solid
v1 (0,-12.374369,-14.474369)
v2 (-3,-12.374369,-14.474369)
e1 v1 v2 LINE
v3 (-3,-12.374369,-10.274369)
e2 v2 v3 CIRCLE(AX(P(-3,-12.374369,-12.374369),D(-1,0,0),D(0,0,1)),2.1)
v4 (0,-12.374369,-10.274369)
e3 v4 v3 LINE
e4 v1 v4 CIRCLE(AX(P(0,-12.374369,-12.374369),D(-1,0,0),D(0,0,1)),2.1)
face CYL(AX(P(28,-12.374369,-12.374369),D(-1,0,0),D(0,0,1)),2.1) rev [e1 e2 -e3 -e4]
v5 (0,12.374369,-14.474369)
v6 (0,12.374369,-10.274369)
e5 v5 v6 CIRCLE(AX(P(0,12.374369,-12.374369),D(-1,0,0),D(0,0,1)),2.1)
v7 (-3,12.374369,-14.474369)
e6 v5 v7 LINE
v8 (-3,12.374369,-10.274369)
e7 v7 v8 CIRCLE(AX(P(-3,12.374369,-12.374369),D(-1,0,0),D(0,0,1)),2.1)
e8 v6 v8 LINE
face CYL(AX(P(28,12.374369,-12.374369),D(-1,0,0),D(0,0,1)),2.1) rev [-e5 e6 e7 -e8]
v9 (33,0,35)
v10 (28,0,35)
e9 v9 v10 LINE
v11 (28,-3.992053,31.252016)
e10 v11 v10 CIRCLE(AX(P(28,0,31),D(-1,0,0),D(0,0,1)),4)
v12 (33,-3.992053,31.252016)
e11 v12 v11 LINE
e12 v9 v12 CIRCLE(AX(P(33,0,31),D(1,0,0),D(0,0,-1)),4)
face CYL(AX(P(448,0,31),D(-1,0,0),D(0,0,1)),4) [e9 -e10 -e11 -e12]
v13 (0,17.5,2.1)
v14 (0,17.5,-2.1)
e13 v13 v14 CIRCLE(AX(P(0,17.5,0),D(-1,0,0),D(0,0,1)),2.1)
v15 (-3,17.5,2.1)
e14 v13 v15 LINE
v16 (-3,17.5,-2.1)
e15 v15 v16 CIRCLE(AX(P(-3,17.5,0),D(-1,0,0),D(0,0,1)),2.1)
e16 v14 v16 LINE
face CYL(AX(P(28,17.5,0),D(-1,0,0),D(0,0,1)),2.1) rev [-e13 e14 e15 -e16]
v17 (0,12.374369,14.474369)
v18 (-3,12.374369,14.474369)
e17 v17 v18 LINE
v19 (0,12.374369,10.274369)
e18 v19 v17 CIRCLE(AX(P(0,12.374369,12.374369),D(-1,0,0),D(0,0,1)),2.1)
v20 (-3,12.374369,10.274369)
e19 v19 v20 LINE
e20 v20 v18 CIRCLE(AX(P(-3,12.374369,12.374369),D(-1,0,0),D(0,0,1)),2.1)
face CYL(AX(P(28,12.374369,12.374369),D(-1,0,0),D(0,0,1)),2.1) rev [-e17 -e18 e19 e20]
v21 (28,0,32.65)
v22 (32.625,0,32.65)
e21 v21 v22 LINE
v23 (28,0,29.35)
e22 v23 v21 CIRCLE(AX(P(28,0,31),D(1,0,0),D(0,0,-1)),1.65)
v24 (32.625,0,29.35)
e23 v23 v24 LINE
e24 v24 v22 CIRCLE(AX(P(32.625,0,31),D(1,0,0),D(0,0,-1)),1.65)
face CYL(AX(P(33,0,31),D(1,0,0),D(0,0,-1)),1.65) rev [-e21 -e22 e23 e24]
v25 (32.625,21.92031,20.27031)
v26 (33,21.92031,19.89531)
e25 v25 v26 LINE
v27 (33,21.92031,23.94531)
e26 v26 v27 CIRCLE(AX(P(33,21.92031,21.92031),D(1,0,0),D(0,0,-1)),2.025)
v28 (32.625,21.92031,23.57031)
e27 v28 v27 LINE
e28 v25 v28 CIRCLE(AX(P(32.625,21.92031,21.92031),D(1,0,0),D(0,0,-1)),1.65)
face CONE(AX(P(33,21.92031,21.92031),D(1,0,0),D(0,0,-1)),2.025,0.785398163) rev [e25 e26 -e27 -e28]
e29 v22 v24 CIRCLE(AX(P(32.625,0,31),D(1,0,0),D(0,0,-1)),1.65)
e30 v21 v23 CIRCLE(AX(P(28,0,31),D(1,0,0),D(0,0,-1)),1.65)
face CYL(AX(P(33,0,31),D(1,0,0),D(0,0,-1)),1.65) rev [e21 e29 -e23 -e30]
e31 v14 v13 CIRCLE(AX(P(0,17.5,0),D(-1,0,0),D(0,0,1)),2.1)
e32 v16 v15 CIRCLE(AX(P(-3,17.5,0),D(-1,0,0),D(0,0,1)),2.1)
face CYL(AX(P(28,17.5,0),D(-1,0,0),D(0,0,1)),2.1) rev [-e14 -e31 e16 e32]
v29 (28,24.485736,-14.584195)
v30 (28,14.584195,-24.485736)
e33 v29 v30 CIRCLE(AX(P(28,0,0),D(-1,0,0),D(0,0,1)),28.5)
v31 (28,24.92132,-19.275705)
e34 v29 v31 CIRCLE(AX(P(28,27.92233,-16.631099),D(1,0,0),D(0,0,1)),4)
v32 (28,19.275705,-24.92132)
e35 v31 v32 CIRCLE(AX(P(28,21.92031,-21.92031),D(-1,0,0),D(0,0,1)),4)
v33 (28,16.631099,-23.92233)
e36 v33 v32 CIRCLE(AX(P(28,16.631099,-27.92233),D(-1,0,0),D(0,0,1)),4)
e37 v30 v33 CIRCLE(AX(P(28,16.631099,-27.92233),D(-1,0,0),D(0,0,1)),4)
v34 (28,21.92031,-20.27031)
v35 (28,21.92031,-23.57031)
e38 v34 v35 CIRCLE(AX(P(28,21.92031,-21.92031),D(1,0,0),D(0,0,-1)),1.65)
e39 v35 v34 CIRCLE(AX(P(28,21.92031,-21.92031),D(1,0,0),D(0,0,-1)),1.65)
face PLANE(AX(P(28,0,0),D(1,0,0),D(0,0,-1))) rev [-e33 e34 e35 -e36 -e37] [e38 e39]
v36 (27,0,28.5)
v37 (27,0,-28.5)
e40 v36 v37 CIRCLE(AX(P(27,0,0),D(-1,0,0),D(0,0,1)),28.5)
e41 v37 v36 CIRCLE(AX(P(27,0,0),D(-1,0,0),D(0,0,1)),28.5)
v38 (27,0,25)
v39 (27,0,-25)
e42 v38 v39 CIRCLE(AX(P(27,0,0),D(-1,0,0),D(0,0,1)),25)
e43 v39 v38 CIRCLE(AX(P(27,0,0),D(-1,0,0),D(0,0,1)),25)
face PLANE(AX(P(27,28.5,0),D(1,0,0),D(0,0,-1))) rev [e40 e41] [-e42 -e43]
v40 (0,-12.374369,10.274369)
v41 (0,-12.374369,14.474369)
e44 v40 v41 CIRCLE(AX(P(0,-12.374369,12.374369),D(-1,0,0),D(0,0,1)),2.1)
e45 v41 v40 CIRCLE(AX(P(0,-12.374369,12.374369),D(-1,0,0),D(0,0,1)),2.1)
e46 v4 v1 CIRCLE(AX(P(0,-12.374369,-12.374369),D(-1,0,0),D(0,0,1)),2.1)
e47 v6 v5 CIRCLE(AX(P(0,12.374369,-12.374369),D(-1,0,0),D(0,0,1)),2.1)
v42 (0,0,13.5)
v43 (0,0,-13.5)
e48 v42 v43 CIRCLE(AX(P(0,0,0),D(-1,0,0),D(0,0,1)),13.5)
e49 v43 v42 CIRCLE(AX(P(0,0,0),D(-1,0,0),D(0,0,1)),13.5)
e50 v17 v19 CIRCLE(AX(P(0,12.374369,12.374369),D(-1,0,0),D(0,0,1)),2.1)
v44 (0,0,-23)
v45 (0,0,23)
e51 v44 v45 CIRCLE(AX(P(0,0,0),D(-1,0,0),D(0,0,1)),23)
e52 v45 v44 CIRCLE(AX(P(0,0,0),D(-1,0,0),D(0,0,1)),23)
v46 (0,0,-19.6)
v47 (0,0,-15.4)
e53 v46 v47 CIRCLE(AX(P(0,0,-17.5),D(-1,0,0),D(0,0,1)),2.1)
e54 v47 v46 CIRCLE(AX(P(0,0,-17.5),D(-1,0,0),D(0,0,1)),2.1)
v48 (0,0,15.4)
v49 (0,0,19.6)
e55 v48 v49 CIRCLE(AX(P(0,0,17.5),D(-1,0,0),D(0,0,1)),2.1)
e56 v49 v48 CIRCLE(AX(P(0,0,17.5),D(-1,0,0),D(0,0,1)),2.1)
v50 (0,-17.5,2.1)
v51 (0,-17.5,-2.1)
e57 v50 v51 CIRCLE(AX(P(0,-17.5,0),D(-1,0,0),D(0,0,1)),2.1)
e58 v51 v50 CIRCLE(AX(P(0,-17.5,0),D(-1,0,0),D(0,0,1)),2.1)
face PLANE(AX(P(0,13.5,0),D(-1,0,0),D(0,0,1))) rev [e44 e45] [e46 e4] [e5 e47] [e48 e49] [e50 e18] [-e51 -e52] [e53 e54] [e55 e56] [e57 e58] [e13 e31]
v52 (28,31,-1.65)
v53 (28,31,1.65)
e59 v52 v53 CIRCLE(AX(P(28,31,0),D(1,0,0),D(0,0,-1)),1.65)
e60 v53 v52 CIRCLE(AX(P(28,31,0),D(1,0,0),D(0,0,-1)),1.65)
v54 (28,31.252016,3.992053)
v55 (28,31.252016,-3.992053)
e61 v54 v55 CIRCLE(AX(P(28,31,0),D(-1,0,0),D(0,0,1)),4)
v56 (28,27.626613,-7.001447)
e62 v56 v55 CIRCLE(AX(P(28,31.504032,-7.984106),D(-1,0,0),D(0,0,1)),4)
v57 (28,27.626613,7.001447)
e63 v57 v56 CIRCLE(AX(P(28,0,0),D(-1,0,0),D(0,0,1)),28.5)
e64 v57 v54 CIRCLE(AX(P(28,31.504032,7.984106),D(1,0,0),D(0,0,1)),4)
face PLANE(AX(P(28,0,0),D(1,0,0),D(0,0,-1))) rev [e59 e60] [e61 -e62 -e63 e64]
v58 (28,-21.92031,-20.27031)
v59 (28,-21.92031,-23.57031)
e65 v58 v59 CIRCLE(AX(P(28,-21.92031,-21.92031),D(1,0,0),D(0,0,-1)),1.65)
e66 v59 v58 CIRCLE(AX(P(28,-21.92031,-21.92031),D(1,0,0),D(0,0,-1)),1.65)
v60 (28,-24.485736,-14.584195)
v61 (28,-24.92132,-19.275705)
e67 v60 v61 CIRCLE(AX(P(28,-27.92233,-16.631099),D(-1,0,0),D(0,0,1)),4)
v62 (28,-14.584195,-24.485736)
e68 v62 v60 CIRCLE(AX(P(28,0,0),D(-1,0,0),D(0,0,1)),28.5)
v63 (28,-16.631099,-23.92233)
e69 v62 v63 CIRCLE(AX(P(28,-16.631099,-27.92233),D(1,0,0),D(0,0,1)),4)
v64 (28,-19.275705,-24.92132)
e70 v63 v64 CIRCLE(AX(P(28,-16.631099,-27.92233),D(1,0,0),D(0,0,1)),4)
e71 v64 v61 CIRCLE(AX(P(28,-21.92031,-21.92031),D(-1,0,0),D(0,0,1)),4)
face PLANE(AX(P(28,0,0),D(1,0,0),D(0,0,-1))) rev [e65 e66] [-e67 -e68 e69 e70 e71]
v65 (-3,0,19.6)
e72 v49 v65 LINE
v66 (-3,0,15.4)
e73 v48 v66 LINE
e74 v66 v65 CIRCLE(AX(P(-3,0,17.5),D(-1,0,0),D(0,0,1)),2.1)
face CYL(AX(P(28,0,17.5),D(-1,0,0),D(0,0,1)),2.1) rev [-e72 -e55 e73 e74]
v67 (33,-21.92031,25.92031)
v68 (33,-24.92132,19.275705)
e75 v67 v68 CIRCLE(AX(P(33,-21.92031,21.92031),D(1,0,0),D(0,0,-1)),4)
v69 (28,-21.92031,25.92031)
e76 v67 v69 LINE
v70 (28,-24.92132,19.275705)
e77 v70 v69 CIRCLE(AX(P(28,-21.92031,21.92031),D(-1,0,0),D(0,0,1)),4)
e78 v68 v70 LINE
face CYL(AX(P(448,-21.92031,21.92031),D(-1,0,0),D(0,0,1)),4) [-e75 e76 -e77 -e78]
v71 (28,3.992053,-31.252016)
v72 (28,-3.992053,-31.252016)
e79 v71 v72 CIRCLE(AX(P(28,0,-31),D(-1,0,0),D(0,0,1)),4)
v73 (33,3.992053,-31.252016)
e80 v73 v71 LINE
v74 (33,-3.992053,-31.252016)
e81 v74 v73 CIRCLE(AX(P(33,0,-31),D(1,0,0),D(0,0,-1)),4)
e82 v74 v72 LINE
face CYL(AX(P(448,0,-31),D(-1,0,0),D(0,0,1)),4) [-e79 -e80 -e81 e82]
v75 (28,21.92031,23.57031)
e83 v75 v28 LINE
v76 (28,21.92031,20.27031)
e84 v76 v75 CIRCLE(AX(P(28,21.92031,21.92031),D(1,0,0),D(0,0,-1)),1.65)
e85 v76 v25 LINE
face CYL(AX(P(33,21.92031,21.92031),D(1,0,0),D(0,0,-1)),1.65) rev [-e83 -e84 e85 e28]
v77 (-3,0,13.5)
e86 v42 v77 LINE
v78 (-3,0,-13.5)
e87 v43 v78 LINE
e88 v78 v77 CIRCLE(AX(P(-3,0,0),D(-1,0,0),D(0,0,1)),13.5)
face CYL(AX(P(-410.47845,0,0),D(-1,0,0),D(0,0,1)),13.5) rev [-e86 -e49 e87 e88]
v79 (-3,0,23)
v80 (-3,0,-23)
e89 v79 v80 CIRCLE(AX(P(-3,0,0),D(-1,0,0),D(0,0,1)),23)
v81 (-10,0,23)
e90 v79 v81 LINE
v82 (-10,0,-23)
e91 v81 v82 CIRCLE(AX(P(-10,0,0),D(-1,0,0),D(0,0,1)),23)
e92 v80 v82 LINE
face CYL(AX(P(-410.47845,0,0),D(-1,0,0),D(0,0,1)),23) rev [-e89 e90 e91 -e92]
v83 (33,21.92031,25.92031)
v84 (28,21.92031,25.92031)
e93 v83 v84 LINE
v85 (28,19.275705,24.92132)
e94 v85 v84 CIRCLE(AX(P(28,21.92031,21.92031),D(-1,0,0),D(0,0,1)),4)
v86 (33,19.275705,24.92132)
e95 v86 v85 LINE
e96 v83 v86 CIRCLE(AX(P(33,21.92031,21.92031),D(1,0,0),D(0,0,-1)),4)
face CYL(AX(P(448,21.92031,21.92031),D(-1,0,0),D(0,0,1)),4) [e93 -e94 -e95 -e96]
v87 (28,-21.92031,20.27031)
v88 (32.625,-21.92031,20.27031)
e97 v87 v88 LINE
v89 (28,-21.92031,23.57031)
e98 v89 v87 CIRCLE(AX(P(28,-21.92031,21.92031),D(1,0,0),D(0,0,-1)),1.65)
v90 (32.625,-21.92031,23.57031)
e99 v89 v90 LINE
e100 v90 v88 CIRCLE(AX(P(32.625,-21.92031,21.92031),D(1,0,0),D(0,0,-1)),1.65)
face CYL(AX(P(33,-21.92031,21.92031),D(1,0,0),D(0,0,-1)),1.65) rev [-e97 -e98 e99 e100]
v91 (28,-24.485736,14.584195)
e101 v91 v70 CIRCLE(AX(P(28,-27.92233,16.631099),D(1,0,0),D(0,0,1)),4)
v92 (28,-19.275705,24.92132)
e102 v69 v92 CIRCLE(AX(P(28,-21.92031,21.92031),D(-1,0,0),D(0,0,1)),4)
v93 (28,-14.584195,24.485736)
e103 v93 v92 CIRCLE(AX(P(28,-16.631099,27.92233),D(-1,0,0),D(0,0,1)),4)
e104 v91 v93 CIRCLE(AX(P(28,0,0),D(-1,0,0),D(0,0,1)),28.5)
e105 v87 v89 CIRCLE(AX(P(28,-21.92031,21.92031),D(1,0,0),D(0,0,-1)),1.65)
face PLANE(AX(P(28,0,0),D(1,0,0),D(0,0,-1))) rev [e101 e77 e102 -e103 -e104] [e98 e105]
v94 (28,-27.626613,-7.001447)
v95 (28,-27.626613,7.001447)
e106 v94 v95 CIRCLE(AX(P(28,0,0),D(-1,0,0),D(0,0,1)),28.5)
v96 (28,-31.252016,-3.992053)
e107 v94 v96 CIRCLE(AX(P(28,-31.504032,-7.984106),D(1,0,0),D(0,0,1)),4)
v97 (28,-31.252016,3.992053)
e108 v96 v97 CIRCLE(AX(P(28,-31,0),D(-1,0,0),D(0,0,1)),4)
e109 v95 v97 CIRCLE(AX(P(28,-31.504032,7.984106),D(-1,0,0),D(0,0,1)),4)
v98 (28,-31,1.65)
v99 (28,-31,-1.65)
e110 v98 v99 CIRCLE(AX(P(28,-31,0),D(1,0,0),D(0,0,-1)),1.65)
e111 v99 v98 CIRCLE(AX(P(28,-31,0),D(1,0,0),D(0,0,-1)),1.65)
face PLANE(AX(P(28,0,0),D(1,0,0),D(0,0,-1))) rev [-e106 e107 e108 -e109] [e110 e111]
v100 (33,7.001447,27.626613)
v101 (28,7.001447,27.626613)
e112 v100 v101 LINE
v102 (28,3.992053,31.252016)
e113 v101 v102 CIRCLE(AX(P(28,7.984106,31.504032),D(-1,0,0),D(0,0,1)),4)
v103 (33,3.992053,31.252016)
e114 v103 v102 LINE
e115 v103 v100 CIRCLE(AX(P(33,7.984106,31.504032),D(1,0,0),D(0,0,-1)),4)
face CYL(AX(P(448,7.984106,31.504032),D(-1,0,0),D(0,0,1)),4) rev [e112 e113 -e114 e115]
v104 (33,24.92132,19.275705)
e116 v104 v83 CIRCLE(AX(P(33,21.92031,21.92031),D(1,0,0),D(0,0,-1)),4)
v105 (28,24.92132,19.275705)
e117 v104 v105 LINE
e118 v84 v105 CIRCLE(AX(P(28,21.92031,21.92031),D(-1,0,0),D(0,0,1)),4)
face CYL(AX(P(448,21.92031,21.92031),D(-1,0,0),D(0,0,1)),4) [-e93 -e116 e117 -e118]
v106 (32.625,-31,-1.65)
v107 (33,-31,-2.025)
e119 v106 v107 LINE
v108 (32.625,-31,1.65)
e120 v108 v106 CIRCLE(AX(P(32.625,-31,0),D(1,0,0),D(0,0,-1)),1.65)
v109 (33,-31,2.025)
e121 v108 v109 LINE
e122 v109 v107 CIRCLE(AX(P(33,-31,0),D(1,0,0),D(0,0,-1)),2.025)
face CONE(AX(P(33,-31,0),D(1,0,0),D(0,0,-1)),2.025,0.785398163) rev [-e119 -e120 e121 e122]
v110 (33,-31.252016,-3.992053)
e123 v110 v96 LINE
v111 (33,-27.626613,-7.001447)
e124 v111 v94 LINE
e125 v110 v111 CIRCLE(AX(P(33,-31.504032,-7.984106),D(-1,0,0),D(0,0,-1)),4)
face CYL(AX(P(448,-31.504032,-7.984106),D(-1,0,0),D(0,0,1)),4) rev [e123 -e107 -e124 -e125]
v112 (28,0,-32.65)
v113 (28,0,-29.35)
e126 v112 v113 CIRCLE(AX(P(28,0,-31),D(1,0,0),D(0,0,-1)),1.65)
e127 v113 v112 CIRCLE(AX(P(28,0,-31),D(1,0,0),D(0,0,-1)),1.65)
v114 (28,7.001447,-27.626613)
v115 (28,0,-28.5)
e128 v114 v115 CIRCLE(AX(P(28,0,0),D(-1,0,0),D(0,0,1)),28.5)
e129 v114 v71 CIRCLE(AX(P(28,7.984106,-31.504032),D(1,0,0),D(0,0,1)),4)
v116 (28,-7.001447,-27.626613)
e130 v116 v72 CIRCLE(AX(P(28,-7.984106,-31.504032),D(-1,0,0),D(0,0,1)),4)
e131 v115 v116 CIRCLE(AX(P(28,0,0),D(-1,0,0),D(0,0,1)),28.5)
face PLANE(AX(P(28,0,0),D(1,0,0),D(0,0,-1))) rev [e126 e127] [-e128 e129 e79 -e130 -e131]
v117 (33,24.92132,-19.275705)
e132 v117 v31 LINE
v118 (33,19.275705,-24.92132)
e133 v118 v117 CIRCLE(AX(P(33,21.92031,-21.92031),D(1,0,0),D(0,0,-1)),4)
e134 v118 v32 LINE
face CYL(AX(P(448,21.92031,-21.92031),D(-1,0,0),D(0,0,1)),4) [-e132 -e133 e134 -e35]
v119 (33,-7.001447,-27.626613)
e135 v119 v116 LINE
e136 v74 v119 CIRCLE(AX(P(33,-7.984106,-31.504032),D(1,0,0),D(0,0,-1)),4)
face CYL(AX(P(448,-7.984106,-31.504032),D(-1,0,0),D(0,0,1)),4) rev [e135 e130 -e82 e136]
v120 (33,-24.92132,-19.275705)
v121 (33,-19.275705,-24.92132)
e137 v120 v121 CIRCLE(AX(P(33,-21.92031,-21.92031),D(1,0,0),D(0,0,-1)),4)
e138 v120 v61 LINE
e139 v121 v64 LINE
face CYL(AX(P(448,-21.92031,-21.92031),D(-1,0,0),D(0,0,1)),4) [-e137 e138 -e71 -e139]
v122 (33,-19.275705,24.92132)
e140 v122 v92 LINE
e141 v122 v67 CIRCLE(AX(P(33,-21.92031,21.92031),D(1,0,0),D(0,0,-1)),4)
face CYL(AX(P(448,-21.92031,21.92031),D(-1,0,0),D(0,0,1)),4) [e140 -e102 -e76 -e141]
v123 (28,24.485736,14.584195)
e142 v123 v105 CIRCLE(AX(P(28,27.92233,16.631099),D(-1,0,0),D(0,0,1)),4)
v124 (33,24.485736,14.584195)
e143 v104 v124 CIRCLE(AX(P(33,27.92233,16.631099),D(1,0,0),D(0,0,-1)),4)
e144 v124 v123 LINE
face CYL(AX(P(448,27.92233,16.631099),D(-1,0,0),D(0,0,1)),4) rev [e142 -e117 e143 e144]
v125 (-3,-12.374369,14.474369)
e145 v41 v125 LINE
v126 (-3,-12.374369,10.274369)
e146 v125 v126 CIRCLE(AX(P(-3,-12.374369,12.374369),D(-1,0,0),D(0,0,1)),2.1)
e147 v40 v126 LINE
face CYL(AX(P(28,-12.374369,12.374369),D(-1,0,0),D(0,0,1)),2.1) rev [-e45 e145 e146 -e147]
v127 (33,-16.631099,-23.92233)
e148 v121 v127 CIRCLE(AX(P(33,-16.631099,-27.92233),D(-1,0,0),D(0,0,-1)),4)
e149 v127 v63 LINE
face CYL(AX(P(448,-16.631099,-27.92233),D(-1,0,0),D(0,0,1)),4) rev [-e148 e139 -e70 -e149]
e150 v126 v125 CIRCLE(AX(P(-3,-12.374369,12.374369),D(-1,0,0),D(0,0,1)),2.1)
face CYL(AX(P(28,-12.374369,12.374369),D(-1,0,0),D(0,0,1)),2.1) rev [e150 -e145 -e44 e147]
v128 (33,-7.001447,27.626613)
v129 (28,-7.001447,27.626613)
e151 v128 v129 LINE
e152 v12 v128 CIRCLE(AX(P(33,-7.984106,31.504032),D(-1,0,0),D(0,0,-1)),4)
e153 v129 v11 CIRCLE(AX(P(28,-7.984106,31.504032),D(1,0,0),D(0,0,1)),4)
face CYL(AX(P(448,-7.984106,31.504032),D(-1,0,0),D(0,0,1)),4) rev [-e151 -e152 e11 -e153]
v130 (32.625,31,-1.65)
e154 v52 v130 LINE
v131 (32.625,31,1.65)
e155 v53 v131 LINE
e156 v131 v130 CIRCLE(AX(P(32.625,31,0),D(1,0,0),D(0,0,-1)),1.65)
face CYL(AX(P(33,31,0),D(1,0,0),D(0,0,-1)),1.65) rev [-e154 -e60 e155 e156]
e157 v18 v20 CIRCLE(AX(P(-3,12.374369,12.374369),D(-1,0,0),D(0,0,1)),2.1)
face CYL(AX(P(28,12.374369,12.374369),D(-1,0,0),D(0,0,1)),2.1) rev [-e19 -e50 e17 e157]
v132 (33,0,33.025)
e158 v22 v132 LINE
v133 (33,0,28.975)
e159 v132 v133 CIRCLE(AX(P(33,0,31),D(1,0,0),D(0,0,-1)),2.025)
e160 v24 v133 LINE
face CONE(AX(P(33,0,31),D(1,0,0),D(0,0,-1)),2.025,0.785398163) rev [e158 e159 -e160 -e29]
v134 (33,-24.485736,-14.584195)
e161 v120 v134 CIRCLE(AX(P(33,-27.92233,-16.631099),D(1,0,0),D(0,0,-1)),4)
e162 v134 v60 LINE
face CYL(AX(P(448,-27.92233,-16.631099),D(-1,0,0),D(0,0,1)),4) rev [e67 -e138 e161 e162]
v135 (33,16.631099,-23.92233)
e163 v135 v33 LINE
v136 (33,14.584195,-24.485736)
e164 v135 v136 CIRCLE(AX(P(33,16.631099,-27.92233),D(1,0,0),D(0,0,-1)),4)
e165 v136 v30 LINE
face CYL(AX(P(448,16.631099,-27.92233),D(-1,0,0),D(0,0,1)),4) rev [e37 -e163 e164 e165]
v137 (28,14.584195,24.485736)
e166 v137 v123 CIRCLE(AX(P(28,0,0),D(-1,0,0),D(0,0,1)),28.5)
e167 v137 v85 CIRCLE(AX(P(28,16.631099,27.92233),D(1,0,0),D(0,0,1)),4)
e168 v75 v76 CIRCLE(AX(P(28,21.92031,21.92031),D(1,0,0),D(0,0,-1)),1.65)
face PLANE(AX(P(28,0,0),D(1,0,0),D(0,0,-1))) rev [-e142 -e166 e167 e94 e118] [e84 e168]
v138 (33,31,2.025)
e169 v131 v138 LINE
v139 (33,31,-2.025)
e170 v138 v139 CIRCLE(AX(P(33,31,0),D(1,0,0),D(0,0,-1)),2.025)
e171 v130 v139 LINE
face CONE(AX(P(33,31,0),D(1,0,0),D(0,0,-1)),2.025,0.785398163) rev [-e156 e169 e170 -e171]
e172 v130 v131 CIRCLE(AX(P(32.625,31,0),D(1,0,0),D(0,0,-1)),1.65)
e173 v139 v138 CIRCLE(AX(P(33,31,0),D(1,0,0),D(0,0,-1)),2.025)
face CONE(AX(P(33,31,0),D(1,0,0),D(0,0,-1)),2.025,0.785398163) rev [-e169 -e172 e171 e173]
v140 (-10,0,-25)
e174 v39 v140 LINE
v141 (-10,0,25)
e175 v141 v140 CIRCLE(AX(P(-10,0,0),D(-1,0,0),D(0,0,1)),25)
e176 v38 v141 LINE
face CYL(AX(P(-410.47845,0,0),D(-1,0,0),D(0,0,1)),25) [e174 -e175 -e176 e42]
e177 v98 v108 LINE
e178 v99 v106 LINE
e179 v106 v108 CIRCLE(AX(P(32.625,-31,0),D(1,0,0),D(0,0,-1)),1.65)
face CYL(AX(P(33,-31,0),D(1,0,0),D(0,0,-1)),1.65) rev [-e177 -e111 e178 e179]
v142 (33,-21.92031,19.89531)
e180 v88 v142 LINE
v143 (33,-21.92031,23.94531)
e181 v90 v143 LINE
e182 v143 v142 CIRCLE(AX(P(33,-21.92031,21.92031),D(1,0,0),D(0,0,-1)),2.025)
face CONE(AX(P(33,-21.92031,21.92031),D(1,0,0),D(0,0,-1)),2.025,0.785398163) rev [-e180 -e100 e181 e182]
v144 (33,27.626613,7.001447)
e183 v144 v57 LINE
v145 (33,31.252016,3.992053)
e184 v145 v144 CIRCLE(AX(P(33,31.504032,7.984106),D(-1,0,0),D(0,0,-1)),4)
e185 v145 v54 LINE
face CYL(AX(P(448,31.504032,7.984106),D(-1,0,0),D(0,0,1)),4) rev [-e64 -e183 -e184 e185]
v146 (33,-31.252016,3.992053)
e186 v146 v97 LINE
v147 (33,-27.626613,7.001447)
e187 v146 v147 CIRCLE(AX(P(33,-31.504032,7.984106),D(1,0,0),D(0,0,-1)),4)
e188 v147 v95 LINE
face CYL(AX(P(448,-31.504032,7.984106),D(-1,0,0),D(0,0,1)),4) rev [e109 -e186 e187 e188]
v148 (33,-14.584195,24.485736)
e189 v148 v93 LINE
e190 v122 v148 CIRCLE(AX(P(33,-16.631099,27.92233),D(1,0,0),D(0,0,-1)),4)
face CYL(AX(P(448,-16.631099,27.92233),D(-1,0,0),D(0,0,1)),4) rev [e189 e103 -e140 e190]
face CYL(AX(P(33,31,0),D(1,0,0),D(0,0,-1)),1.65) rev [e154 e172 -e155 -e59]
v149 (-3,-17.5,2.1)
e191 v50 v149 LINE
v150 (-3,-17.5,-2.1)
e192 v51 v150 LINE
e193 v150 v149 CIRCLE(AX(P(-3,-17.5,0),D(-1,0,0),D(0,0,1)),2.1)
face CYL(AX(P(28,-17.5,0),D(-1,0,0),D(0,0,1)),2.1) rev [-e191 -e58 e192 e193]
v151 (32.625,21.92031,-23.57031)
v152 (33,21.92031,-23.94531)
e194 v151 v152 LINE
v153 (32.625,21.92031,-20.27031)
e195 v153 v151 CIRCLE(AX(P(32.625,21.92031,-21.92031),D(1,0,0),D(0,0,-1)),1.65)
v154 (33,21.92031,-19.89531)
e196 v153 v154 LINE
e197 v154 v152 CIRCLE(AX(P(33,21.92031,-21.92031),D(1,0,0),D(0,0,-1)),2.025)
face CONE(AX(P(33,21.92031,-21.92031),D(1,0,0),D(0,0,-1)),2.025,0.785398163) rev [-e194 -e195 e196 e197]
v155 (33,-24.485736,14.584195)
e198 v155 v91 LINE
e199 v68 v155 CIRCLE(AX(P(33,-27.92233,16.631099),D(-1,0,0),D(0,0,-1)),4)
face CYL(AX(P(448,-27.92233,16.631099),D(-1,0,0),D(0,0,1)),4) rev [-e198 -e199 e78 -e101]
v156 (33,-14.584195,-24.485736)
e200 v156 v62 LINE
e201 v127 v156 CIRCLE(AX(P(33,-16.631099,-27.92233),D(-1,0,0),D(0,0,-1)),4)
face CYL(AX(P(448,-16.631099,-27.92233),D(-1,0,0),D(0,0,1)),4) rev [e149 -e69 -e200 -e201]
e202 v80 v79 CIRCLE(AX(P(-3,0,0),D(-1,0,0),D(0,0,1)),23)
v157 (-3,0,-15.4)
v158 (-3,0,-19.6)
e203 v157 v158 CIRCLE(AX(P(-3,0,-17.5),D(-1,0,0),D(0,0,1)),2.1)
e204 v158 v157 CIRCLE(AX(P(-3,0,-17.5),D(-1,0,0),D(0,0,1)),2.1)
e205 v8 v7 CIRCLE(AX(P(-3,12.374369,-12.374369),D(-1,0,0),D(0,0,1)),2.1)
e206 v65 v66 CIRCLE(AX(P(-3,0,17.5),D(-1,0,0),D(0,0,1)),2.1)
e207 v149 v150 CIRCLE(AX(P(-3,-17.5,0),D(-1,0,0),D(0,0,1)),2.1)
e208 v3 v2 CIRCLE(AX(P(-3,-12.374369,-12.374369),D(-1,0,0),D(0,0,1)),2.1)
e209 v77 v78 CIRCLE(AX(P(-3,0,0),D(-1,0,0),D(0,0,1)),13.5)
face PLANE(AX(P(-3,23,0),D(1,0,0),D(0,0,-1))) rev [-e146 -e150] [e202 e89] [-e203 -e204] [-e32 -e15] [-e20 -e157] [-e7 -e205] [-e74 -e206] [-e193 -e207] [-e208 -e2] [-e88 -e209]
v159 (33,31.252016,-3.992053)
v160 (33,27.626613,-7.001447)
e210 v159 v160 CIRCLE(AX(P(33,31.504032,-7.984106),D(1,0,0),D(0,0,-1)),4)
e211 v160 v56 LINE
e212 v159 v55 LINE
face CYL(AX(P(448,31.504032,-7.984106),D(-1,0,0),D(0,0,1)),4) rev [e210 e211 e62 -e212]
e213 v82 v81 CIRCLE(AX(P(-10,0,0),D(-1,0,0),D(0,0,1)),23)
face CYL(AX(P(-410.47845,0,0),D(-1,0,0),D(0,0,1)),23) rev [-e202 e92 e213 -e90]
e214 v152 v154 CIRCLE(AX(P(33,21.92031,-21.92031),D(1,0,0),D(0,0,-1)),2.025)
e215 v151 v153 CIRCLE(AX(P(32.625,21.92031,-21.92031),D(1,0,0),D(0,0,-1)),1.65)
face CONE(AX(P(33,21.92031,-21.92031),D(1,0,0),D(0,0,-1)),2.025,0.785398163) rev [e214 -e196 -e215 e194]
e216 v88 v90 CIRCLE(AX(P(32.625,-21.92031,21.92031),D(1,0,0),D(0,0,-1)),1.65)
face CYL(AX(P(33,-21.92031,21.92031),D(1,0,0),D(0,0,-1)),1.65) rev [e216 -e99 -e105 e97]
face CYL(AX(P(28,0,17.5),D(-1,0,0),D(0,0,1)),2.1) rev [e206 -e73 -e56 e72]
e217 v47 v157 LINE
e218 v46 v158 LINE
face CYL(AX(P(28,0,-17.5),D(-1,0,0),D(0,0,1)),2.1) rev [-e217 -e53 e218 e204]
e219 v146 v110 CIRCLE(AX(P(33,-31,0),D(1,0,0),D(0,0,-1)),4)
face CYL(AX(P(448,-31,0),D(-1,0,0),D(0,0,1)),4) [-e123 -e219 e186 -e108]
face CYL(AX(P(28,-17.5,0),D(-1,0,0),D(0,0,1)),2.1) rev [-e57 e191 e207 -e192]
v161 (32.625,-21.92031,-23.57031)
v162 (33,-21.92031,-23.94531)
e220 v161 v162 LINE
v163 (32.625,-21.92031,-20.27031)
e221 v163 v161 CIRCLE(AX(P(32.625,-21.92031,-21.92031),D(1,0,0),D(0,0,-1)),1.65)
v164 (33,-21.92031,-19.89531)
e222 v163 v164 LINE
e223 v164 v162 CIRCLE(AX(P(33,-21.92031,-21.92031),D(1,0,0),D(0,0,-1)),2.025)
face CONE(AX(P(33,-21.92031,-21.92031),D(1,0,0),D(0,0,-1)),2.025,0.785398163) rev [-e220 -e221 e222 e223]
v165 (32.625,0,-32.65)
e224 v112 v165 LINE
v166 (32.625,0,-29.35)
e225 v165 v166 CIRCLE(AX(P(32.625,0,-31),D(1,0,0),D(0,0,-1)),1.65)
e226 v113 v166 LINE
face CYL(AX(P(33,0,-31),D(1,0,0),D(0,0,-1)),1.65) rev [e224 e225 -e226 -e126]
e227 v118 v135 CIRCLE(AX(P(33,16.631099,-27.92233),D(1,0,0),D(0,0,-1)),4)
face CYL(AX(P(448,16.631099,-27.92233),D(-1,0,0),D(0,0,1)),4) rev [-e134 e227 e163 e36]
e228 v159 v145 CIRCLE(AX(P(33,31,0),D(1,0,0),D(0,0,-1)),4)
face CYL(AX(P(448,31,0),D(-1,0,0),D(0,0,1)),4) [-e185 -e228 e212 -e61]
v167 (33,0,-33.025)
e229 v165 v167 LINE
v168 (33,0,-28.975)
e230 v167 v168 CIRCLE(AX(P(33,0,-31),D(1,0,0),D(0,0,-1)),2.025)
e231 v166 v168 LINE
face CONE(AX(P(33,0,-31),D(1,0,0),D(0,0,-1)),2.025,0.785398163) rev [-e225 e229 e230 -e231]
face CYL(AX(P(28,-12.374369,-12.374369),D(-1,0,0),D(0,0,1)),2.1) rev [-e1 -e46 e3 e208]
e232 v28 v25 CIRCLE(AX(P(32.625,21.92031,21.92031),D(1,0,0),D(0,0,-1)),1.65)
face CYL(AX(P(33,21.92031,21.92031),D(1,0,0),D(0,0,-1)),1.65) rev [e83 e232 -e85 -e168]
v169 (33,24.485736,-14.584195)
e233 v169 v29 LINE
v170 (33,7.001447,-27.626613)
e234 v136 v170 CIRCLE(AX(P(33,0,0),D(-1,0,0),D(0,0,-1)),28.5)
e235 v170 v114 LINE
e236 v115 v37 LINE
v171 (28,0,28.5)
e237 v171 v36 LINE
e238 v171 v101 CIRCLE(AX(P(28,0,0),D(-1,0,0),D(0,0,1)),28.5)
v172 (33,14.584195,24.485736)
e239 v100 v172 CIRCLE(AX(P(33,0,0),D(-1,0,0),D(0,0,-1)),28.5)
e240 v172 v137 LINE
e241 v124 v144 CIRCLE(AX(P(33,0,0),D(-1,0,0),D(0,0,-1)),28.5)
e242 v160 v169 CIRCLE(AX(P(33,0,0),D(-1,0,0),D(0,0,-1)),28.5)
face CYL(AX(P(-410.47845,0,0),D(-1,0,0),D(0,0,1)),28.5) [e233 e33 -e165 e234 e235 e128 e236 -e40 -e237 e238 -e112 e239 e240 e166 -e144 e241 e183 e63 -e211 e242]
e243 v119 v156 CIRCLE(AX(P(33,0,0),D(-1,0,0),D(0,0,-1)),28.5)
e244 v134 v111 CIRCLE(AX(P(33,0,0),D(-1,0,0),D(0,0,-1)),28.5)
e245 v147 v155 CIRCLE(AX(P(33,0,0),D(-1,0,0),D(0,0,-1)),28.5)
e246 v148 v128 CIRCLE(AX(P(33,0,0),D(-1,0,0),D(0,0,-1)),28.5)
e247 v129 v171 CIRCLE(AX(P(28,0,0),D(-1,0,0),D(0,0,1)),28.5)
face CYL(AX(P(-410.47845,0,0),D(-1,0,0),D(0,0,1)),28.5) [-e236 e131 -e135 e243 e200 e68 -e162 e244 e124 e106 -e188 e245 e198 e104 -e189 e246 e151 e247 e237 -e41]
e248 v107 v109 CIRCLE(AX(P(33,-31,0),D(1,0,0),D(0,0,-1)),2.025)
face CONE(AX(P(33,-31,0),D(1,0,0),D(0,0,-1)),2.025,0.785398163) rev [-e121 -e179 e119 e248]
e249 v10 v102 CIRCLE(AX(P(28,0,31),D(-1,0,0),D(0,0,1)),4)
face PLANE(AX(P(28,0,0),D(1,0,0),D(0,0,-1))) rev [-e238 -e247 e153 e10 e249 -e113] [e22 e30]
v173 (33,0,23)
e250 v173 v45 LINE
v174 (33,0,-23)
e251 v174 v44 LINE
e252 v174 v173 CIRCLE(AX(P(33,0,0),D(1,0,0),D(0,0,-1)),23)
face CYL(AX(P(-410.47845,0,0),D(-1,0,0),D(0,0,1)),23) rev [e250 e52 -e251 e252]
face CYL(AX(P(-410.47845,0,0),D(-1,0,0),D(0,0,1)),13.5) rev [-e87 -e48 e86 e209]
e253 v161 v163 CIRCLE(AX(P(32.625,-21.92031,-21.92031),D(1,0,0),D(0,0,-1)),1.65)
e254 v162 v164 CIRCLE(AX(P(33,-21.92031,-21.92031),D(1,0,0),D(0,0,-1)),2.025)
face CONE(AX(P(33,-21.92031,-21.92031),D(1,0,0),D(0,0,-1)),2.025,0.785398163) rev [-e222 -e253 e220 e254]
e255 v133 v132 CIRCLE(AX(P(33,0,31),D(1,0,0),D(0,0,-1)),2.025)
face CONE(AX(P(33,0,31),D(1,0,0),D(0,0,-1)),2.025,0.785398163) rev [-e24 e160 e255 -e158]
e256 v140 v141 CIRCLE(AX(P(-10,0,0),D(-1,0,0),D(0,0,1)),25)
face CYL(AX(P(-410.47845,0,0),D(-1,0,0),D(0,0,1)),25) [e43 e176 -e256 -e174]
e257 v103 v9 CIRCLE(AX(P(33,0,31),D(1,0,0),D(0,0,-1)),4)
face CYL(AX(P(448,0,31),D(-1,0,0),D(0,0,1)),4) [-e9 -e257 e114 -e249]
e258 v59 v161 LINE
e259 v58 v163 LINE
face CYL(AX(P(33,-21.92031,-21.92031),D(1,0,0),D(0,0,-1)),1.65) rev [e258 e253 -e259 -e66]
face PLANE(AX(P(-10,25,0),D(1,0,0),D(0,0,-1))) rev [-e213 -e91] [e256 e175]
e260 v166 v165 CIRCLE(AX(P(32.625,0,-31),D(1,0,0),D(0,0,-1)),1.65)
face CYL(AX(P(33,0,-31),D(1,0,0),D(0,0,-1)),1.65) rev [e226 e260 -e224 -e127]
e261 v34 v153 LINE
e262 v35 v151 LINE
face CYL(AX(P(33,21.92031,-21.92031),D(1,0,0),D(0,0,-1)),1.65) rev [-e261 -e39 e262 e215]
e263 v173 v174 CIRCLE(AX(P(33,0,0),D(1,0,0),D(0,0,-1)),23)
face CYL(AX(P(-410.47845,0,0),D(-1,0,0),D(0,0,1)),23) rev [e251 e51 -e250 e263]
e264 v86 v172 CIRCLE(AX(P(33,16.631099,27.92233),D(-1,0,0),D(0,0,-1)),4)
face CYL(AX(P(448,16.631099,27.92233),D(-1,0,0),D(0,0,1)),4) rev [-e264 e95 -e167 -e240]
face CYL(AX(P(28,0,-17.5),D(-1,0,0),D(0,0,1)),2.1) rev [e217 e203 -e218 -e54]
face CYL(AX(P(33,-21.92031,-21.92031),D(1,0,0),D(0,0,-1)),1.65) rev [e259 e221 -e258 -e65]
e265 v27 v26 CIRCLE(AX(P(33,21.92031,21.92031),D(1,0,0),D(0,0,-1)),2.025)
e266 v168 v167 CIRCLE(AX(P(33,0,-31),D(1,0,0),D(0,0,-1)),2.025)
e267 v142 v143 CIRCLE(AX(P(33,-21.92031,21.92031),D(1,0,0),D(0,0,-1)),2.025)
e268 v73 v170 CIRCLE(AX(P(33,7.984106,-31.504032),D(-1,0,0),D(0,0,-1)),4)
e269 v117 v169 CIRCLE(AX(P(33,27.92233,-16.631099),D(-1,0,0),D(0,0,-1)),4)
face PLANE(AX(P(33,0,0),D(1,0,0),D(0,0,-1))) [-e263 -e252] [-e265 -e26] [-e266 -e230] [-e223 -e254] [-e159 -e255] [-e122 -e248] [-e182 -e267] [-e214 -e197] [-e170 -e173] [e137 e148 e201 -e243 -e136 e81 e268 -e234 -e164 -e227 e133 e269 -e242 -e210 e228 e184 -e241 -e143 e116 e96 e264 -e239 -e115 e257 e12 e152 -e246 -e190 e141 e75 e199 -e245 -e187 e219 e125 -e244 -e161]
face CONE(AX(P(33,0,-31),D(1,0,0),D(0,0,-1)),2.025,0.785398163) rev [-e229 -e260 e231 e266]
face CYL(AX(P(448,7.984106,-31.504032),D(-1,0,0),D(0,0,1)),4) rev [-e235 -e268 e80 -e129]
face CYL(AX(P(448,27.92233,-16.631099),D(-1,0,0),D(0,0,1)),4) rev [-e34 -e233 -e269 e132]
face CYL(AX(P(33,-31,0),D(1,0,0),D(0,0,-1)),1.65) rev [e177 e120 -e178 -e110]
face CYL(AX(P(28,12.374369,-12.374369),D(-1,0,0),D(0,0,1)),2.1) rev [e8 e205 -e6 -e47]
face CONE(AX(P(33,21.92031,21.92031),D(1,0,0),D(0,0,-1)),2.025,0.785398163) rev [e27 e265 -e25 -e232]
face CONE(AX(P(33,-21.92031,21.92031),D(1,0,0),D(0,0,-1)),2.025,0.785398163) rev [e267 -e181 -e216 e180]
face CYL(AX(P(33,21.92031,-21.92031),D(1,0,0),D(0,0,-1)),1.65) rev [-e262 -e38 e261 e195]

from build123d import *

# Parameters (mm, degrees)
SKETCH_2_R                   = 2.1
CUT_EXTRUDE_1_DEPTH          = 51.847812146
EXTRUDE_START                = 5
SKETCH_3_R                   = 35
SKETCH_3_R_2                 = 23
EXTRUDE_1_DEPTH              = 5
HOLE_WIZARD_M4_1_D           = 3.3
HOLE_WIZARD_M4_1_CSINK_D     = 4.05
HOLE_WIZARD_M4_1_CSINK_ANGLE = 90
CUT_EXTRUDE_3_DEPTH          = 420


with BuildPart() as part:
    # 草图1 → 旋转1 (revolve)
    with BuildSketch(Plane.XY, mode=Mode.PRIVATE) as revolve_1_sk:
        Polygon((0, 13.5), (0, 23), (28, 23), (28, 28.5), (27, 28.5), (27, 25), (-10, 25), (-10, 23), (-3, 23), (-3, 13.5), align=None)
    revolve(revolve_1_sk.sketch.rotate(Axis((-410.478449984, 0, 0), (1, 0, 0)), 90), axis=Axis((-410.478449984, 0, 0), (1, 0, 0)))

    # 草图2 → 切除-拉伸1 (cut, through all)
    with BuildSketch(Plane.ZY.offset(3)):
        with Locations((0, 17.5)):
            Circle(SKETCH_2_R)
        with Locations((12.374368671, 12.374368671)):
            Circle(SKETCH_2_R)
        with Locations((17.5, 0)):
            Circle(SKETCH_2_R)
        with Locations((12.374368671, -12.374368671)):
            Circle(SKETCH_2_R)
        with Locations((0, -17.5)):
            Circle(SKETCH_2_R)
        with Locations((-12.374368671, -12.374368671)):
            Circle(SKETCH_2_R)
        with Locations((-17.5, 0)):
            Circle(SKETCH_2_R)
        with Locations((-12.374368671, 12.374368671)):
            Circle(SKETCH_2_R)
    extrude(amount=-CUT_EXTRUDE_1_DEPTH, mode=Mode.SUBTRACT)

    # 草图3 → 凸台-拉伸1 (add)
    with BuildSketch(Plane(origin=(28, 0, 0), x_dir=(0, 0, -1), z_dir=(1, 0, 0)).offset(EXTRUDE_START)):
        Circle(SKETCH_3_R)
        with Locations(Location((0, 0, 0), (0, 0, 180))):
            Circle(SKETCH_3_R_2, mode=Mode.SUBTRACT)
    extrude(amount=-EXTRUDE_1_DEPTH)

    # M4 螺纹孔1 (through all)
    with Locations(Plane(origin=(33, 0, 0), x_dir=(0, 0, -1), z_dir=(1, 0, 0))):
        with Locations((-21.920310217, 21.920310217), (0, 31), (21.920310217, 21.920310217), (31, 0), (21.920310217, -21.920310217), (0, -31), (-21.920310217, -21.920310217), (-31, 0)):
            CounterSinkHole(HOLE_WIZARD_M4_1_D / 2, HOLE_WIZARD_M4_1_CSINK_D / 2, counter_sink_angle=HOLE_WIZARD_M4_1_CSINK_ANGLE)

    # 草图9 → 切除-拉伸3 (cut)
    with BuildSketch(Plane.ZY.offset(-28)):
        with BuildLine():
            ThreePointArc((0, 35), (2.737876502, 33.916167392), (3.99205309, 31.252016129))
            ThreePointArc((3.99205309, 31.252016129), (4.90631025, 28.949199149), (7.001446957, 27.626612903))
            ThreePointArc((7.001446957, 27.626612903), (10.906477822, 26.330566677), (14.584194703, 24.485735947))
            ThreePointArc((14.584194703, 24.485735947), (17.00088978, 23.939460276), (19.27570472, 24.921320341))
            ThreePointArc((19.27570472, 24.921320341), (22.046380914, 25.918322996), (24.748737342, 24.748737342))
            ThreePointArc((24.748737342, 24.748737342), (13.393920133, 32.335783638), (0, 35))
        make_face()
        with BuildLine():
            ThreePointArc((-3.99205309, 31.252016129), (-2.737876502, 33.916167392), (0, 35))
            ThreePointArc((0, 35), (-13.393920111, 32.335783647), (-24.748737308, 24.748737375))
            ThreePointArc((-24.748737308, 24.748737375), (-22.04638089, 25.918322996), (-19.27570472, 24.921320341))
            ThreePointArc((-19.27570472, 24.921320341), (-17.00088978, 23.939460276), (-14.584194703, 24.485735947))
            ThreePointArc((-14.584194703, 24.485735947), (-10.906477822, 26.330566677), (-7.001446957, 27.626612903))
            ThreePointArc((-7.001446957, 27.626612903), (-4.90631025, 28.949199149), (-3.99205309, 31.252016129))
        make_face()
        with BuildLine():
            ThreePointArc((35, 0), (32.335783638, 13.393920133), (24.748737342, 24.748737342))
            ThreePointArc((24.748737342, 24.748737342), (25.918322996, 22.046380914), (24.921320341, 19.27570472))
            ThreePointArc((24.921320341, 19.27570472), (23.939460276, 17.00088978), (24.485735947, 14.584194703))
            ThreePointArc((24.485735947, 14.584194703), (26.330566677, 10.906477822), (27.626612903, 7.001446957))
            ThreePointArc((27.626612903, 7.001446957), (28.949199149, 4.90631025), (31.252016129, 3.99205309))
            ThreePointArc((31.252016129, 3.99205309), (33.916167392, 2.737876502), (35, 0))
        make_face()
        with BuildLine():
            ThreePointArc((-24.921320341, 19.27570472), (-25.918322995, 22.046380937), (-24.748737308, 24.748737375))
            ThreePointArc((-24.748737308, 24.748737375), (-32.335783614, 13.39392019), (-35, 7.6e-08))
            ThreePointArc((-35, 7.6e-08), (-33.916167366, 2.73787653), (-31.252016129, 3.99205309))
            ThreePointArc((-31.252016129, 3.99205309), (-28.949199149, 4.90631025), (-27.626612903, 7.001446957))
            ThreePointArc((-27.626612903, 7.001446957), (-26.330566677, 10.906477822), (-24.485735947, 14.584194703))
            ThreePointArc((-24.485735947, 14.584194703), (-23.939460276, 17.00088978), (-24.921320341, 19.27570472))
        make_face()
        with BuildLine():
            ThreePointArc((24.748737305, -24.748737378), (32.335783628, -13.393920156), (35, 0))
            ThreePointArc((35, 0), (33.916167392, -2.737876502), (31.252016129, -3.99205309))
            ThreePointArc((31.252016129, -3.99205309), (28.949199149, -4.90631025), (27.626612903, -7.001446957))
            ThreePointArc((27.626612903, -7.001446957), (26.330566677, -10.906477822), (24.485735947, -14.584194703))
            ThreePointArc((24.485735947, -14.584194703), (23.939460276, -17.00088978), (24.921320341, -19.27570472))
            ThreePointArc((24.921320341, -19.27570472), (25.918322995, -22.046380939), (24.748737305, -24.748737378))
        make_face()
        with BuildLine():
            ThreePointArc((-31.252016129, -3.99205309), (-33.916167418, -2.737876475), (-35, 7.6e-08))
            ThreePointArc((-35, 7.6e-08), (-32.335783652, -13.393920098), (-24.748737342, -24.748737342))
            ThreePointArc((-24.748737342, -24.748737342), (-25.918322996, -22.046380914), (-24.921320341, -19.27570472))
            ThreePointArc((-24.921320341, -19.27570472), (-23.939460276, -17.00088978), (-24.485735947, -14.584194703))
            ThreePointArc((-24.485735947, -14.584194703), (-26.330566677, -10.906477822), (-27.626612903, -7.001446957))
            ThreePointArc((-27.626612903, -7.001446957), (-28.949199149, -4.90631025), (-31.252016129, -3.99205309))
        make_face()
        with BuildLine():
            ThreePointArc((0, -35), (13.393920109, -32.335783648), (24.748737305, -24.748737378))
            ThreePointArc((24.748737305, -24.748737378), (22.046380888, -25.918322996), (19.27570472, -24.921320341))
            ThreePointArc((19.27570472, -24.921320341), (17.00088978, -23.939460276), (14.584194703, -24.485735947))
            ThreePointArc((14.584194703, -24.485735947), (10.906477822, -26.330566677), (7.001446957, -27.626612903))
            ThreePointArc((7.001446957, -27.626612903), (4.90631025, -28.949199149), (3.99205309, -31.252016129))
            ThreePointArc((3.99205309, -31.252016129), (2.737876502, -33.916167392), (0, -35))
        make_face()
        with BuildLine():
            ThreePointArc((-19.27570472, -24.921320341), (-22.046380914, -25.918322996), (-24.748737342, -24.748737342))
            ThreePointArc((-24.748737342, -24.748737342), (-13.393920133, -32.335783638), (0, -35))
            ThreePointArc((0, -35), (-2.737876502, -33.916167392), (-3.99205309, -31.252016129))
            ThreePointArc((-3.99205309, -31.252016129), (-4.90631025, -28.949199149), (-7.001446957, -27.626612903))
            ThreePointArc((-7.001446957, -27.626612903), (-10.906477822, -26.330566677), (-14.584194703, -24.485735947))
            ThreePointArc((-14.584194703, -24.485735947), (-17.00088978, -23.939460276), (-19.27570472, -24.921320341))
        make_face()
    extrude(amount=-CUT_EXTRUDE_3_DEPTH, mode=Mode.SUBTRACT)


solid = part.part
